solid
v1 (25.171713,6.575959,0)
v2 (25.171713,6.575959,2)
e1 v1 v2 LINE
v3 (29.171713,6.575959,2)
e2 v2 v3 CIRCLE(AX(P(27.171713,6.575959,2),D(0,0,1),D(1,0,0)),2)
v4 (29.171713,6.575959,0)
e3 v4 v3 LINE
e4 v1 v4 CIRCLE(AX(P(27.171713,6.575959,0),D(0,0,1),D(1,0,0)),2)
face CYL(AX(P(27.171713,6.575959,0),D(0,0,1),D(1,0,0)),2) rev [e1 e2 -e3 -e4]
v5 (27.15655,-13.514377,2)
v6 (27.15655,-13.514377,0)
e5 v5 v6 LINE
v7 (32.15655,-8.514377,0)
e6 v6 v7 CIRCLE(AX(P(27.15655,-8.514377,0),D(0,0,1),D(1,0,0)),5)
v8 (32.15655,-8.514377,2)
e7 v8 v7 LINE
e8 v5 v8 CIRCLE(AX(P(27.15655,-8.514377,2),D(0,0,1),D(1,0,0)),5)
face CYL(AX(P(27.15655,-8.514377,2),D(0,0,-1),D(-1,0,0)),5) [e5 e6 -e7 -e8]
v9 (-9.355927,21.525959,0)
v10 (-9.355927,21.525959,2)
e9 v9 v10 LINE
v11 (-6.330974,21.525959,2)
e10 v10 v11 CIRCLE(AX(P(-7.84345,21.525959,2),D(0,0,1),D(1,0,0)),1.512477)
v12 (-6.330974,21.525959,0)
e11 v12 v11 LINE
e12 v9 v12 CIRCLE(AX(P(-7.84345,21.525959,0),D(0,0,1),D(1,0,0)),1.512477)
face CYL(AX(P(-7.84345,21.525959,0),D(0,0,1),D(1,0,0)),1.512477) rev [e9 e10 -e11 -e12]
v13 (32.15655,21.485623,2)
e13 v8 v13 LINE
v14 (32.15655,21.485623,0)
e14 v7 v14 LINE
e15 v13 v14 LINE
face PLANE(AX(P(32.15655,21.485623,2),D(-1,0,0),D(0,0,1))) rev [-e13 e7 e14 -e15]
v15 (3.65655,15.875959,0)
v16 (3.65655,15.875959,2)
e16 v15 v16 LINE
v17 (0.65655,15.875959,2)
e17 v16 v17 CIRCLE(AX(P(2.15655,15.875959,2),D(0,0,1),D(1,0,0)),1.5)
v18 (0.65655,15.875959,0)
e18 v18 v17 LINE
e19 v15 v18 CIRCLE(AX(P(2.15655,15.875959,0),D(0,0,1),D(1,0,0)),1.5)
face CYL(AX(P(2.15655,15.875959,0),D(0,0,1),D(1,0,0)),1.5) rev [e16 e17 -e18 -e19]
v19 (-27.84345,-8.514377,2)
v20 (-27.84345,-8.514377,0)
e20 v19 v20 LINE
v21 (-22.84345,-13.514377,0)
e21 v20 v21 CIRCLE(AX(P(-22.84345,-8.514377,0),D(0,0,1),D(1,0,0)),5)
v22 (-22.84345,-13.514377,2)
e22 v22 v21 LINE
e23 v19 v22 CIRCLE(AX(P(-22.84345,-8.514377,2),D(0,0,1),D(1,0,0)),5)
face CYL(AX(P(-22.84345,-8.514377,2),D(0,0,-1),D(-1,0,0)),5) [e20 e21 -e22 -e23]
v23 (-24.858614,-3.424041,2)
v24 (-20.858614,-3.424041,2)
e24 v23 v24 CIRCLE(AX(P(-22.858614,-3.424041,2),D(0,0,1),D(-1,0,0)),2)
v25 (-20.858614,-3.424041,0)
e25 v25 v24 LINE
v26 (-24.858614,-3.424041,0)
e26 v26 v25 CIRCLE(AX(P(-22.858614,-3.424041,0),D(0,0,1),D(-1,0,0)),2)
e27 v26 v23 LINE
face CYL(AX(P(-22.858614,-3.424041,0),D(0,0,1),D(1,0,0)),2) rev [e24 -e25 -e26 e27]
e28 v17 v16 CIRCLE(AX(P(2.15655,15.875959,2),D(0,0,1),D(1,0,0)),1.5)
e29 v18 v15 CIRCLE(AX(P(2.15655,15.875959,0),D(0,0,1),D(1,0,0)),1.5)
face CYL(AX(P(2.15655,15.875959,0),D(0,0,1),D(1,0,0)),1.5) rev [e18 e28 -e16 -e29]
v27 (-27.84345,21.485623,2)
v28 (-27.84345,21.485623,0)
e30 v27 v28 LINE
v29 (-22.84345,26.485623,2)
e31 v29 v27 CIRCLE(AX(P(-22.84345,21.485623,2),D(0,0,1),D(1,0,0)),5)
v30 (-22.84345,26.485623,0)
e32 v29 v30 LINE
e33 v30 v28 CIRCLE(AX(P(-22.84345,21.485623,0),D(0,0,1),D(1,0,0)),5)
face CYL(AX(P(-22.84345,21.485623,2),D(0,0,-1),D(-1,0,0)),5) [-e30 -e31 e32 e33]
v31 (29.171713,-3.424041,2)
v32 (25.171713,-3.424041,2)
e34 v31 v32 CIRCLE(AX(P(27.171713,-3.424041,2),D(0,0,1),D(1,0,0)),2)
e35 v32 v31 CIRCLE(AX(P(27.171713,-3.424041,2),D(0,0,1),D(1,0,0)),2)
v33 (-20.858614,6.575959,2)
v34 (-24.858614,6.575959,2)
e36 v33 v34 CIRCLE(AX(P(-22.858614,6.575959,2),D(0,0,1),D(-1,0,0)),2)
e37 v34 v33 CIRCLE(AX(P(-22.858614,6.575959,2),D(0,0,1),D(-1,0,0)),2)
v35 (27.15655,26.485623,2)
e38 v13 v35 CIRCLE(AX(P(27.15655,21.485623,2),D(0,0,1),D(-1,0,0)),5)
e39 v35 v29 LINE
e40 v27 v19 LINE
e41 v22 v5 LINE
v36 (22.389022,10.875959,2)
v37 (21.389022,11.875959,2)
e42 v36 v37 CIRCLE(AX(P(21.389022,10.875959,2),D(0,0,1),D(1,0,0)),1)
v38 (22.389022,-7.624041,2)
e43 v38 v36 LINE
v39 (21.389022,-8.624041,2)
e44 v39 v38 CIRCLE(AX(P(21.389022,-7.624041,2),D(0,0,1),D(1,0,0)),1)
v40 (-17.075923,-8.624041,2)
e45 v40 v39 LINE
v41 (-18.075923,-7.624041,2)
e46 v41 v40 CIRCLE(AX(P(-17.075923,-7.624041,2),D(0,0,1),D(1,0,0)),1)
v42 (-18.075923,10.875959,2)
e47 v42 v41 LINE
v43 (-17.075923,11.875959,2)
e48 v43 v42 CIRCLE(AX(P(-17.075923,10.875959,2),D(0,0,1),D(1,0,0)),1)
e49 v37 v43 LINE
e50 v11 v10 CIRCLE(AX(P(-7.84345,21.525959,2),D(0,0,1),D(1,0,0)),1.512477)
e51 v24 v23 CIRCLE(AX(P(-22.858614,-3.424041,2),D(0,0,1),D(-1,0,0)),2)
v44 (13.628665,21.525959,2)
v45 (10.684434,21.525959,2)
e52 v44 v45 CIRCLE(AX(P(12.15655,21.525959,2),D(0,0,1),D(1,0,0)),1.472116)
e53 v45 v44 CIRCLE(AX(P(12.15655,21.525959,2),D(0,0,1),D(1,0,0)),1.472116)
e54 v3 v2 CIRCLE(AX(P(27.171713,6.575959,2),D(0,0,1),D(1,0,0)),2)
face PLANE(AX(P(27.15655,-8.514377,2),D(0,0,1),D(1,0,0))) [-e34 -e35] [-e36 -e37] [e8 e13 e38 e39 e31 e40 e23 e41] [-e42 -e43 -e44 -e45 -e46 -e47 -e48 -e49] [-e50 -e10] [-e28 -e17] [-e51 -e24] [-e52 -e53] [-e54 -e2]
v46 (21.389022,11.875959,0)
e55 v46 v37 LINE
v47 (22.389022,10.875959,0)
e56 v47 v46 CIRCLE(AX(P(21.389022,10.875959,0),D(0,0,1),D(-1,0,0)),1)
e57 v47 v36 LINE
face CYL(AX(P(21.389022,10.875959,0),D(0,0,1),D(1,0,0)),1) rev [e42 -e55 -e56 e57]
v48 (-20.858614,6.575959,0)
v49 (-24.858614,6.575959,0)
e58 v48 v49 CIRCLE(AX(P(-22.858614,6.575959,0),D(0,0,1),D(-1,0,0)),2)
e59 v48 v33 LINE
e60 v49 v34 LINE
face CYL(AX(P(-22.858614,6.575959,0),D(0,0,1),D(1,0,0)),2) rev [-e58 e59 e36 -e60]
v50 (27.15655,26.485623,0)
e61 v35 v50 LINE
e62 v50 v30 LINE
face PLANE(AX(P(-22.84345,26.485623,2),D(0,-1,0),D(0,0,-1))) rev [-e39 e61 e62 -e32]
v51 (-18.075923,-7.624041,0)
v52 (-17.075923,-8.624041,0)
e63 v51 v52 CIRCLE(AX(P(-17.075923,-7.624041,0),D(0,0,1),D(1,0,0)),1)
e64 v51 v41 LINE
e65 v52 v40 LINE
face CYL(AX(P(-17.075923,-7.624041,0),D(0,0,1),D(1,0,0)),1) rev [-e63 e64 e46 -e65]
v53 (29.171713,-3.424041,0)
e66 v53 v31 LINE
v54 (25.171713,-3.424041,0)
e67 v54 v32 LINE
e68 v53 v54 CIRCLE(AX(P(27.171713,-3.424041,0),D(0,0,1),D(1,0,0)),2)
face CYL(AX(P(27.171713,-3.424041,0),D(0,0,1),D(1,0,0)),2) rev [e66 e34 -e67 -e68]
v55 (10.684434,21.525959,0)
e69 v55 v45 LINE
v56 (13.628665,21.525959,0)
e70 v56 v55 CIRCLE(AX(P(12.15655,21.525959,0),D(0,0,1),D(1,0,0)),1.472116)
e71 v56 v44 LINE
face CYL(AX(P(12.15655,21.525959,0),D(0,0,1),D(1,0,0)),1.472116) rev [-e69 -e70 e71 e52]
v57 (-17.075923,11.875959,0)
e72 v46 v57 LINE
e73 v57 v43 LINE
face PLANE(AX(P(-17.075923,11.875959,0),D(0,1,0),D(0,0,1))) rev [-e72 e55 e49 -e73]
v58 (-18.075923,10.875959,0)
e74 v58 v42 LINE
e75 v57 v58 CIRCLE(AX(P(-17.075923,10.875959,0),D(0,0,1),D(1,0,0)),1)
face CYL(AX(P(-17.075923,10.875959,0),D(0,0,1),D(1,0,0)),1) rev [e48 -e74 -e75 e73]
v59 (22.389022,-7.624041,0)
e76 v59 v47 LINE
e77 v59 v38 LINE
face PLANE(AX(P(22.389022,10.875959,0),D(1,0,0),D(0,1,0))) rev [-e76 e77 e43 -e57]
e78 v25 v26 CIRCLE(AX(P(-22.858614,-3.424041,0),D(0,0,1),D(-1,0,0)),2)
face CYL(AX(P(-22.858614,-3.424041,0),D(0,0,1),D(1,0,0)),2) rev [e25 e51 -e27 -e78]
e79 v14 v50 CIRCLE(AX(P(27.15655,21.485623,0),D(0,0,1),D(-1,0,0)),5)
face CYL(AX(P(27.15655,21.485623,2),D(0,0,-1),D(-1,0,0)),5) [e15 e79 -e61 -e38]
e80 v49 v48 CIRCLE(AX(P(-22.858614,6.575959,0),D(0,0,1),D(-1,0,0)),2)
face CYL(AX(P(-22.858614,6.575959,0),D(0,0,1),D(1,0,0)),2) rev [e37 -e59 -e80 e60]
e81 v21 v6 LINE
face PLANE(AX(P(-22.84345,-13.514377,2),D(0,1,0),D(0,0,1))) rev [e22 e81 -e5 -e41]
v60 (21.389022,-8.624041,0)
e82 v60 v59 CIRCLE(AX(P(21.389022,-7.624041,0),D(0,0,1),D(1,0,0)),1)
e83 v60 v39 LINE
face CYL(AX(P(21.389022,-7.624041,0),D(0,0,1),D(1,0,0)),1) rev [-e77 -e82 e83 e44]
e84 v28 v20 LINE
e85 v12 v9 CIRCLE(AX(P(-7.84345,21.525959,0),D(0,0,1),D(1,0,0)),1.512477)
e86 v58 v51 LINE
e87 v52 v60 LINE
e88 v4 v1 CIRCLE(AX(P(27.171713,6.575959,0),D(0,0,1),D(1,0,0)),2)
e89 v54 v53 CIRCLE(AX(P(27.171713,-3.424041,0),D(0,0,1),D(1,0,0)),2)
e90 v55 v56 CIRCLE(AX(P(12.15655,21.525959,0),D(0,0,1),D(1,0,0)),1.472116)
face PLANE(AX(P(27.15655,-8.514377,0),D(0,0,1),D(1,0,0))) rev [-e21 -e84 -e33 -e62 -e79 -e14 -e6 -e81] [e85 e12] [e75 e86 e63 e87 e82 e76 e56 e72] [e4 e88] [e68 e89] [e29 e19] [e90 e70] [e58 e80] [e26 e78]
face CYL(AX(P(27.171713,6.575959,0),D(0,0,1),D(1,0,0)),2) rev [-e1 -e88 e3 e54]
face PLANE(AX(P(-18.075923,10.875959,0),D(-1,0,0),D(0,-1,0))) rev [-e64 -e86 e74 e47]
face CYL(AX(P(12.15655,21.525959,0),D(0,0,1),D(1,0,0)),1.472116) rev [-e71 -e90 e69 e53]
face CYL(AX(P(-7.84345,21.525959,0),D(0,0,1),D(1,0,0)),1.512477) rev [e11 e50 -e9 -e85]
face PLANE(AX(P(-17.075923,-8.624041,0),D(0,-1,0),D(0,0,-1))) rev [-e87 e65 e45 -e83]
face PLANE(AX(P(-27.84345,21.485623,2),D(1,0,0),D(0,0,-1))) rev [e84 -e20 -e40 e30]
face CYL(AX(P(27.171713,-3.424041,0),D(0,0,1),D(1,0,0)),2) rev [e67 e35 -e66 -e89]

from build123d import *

# Parameters (mm, degrees)
BOSS_EXTRUDE1_DEPTH     = 2
CUT_EXTRUDE1_DEPTH      = 42.707695968
CUT_EXTRUDE1_DEPTH_BACK = 42.707695968
SKETCH3_R               = 1.5
SKETCH3_R_2             = 1.472115529
SKETCH3_R_3             = 1.512476654
CUT_EXTRUDE2_DEPTH      = 42.707695968
SKETCH4_R               = 2
CUT_EXTRUDE3_DEPTH      = 42.707695968


with BuildPart() as part:
    # Sketch1 → Boss-Extrude1 (new body)
    with BuildSketch(Plane.XY):
        with BuildLine():
            Line((-22.843450479, 26.485623003), (27.156549521, 26.485623003))
            ThreePointArc((27.156549521, 26.485623003), (30.692083427, 25.021156909), (32.156549521, 21.485623003))
            Line((32.156549521, 21.485623003), (32.156549521, -8.514376997))
            ThreePointArc((32.156549521, -8.514376997), (30.692083427, -12.049910903), (27.156549521, -13.514376997))
            Line((27.156549521, -13.514376997), (-22.843450479, -13.514376997))
            ThreePointArc((-22.843450479, -13.514376997), (-26.378984385, -12.049910903), (-27.843450479, -8.514376997))
            Line((-27.843450479, -8.514376997), (-27.843450479, 21.485623003))
            ThreePointArc((-27.843450479, 21.485623003), (-26.378984385, 25.021156909), (-22.843450479, 26.485623003))
        make_face()
    extrude(amount=BOSS_EXTRUDE1_DEPTH)

    # Sketch2 → Cut-Extrude1 (cut, two sides: drawn at the far end of the back side and taken through both)
    with BuildSketch(Plane.XY.offset(2).offset(-CUT_EXTRUDE1_DEPTH_BACK)):
        with BuildLine():
            Line((-17.075923419, 11.875959063), (21.38902246, 11.875959063))
            ThreePointArc((21.38902246, 11.875959063), (22.096129242, 11.583065844), (22.38902246, 10.875959063))
            Line((22.38902246, 10.875959063), (22.38902246, -7.624040937))
            ThreePointArc((22.38902246, -7.624040937), (22.096129242, -8.331147718), (21.38902246, -8.624040937))
            Line((21.38902246, -8.624040937), (-17.075923419, -8.624040937))
            ThreePointArc((-17.075923419, -8.624040937), (-17.7830302, -8.331147718), (-18.075923419, -7.624040937))
            Line((-18.075923419, -7.624040937), (-18.075923419, 10.875959063))
            ThreePointArc((-18.075923419, 10.875959063), (-17.7830302, 11.583065844), (-17.075923419, 11.875959063))
        make_face()
    extrude(amount=CUT_EXTRUDE1_DEPTH + CUT_EXTRUDE1_DEPTH_BACK, mode=Mode.SUBTRACT)

    # Sketch3 → Cut-Extrude2 (cut, through all)
    with BuildSketch(Plane.XY.offset(2)):
        with Locations((2.156549521, 15.875959063)):
            Circle(SKETCH3_R)
        with Locations((12.156549521, 21.525959063)):
            Circle(SKETCH3_R_2)
        with Locations((-7.843450479, 21.525959063)):
            Circle(SKETCH3_R_3)
    extrude(amount=-CUT_EXTRUDE2_DEPTH, mode=Mode.SUBTRACT)

    # Sketch4 → Cut-Extrude3 (cut, through all)
    with BuildSketch(Plane.XY.offset(2)):
        with Locations((27.17171292, -3.424040937)):
            Circle(SKETCH4_R)
        with Locations((27.17171292, 6.575959063)):
            Circle(SKETCH4_R)
        with Locations(Location((-22.858613878, -3.424040937, 0), (0, 0, 180))):
            Circle(SKETCH4_R)
        with Locations(Location((-22.858613878, 6.575959063, 0), (0, 0, 180))):
            Circle(SKETCH4_R)
    extrude(amount=-CUT_EXTRUDE3_DEPTH, mode=Mode.SUBTRACT)


solid = part.part
